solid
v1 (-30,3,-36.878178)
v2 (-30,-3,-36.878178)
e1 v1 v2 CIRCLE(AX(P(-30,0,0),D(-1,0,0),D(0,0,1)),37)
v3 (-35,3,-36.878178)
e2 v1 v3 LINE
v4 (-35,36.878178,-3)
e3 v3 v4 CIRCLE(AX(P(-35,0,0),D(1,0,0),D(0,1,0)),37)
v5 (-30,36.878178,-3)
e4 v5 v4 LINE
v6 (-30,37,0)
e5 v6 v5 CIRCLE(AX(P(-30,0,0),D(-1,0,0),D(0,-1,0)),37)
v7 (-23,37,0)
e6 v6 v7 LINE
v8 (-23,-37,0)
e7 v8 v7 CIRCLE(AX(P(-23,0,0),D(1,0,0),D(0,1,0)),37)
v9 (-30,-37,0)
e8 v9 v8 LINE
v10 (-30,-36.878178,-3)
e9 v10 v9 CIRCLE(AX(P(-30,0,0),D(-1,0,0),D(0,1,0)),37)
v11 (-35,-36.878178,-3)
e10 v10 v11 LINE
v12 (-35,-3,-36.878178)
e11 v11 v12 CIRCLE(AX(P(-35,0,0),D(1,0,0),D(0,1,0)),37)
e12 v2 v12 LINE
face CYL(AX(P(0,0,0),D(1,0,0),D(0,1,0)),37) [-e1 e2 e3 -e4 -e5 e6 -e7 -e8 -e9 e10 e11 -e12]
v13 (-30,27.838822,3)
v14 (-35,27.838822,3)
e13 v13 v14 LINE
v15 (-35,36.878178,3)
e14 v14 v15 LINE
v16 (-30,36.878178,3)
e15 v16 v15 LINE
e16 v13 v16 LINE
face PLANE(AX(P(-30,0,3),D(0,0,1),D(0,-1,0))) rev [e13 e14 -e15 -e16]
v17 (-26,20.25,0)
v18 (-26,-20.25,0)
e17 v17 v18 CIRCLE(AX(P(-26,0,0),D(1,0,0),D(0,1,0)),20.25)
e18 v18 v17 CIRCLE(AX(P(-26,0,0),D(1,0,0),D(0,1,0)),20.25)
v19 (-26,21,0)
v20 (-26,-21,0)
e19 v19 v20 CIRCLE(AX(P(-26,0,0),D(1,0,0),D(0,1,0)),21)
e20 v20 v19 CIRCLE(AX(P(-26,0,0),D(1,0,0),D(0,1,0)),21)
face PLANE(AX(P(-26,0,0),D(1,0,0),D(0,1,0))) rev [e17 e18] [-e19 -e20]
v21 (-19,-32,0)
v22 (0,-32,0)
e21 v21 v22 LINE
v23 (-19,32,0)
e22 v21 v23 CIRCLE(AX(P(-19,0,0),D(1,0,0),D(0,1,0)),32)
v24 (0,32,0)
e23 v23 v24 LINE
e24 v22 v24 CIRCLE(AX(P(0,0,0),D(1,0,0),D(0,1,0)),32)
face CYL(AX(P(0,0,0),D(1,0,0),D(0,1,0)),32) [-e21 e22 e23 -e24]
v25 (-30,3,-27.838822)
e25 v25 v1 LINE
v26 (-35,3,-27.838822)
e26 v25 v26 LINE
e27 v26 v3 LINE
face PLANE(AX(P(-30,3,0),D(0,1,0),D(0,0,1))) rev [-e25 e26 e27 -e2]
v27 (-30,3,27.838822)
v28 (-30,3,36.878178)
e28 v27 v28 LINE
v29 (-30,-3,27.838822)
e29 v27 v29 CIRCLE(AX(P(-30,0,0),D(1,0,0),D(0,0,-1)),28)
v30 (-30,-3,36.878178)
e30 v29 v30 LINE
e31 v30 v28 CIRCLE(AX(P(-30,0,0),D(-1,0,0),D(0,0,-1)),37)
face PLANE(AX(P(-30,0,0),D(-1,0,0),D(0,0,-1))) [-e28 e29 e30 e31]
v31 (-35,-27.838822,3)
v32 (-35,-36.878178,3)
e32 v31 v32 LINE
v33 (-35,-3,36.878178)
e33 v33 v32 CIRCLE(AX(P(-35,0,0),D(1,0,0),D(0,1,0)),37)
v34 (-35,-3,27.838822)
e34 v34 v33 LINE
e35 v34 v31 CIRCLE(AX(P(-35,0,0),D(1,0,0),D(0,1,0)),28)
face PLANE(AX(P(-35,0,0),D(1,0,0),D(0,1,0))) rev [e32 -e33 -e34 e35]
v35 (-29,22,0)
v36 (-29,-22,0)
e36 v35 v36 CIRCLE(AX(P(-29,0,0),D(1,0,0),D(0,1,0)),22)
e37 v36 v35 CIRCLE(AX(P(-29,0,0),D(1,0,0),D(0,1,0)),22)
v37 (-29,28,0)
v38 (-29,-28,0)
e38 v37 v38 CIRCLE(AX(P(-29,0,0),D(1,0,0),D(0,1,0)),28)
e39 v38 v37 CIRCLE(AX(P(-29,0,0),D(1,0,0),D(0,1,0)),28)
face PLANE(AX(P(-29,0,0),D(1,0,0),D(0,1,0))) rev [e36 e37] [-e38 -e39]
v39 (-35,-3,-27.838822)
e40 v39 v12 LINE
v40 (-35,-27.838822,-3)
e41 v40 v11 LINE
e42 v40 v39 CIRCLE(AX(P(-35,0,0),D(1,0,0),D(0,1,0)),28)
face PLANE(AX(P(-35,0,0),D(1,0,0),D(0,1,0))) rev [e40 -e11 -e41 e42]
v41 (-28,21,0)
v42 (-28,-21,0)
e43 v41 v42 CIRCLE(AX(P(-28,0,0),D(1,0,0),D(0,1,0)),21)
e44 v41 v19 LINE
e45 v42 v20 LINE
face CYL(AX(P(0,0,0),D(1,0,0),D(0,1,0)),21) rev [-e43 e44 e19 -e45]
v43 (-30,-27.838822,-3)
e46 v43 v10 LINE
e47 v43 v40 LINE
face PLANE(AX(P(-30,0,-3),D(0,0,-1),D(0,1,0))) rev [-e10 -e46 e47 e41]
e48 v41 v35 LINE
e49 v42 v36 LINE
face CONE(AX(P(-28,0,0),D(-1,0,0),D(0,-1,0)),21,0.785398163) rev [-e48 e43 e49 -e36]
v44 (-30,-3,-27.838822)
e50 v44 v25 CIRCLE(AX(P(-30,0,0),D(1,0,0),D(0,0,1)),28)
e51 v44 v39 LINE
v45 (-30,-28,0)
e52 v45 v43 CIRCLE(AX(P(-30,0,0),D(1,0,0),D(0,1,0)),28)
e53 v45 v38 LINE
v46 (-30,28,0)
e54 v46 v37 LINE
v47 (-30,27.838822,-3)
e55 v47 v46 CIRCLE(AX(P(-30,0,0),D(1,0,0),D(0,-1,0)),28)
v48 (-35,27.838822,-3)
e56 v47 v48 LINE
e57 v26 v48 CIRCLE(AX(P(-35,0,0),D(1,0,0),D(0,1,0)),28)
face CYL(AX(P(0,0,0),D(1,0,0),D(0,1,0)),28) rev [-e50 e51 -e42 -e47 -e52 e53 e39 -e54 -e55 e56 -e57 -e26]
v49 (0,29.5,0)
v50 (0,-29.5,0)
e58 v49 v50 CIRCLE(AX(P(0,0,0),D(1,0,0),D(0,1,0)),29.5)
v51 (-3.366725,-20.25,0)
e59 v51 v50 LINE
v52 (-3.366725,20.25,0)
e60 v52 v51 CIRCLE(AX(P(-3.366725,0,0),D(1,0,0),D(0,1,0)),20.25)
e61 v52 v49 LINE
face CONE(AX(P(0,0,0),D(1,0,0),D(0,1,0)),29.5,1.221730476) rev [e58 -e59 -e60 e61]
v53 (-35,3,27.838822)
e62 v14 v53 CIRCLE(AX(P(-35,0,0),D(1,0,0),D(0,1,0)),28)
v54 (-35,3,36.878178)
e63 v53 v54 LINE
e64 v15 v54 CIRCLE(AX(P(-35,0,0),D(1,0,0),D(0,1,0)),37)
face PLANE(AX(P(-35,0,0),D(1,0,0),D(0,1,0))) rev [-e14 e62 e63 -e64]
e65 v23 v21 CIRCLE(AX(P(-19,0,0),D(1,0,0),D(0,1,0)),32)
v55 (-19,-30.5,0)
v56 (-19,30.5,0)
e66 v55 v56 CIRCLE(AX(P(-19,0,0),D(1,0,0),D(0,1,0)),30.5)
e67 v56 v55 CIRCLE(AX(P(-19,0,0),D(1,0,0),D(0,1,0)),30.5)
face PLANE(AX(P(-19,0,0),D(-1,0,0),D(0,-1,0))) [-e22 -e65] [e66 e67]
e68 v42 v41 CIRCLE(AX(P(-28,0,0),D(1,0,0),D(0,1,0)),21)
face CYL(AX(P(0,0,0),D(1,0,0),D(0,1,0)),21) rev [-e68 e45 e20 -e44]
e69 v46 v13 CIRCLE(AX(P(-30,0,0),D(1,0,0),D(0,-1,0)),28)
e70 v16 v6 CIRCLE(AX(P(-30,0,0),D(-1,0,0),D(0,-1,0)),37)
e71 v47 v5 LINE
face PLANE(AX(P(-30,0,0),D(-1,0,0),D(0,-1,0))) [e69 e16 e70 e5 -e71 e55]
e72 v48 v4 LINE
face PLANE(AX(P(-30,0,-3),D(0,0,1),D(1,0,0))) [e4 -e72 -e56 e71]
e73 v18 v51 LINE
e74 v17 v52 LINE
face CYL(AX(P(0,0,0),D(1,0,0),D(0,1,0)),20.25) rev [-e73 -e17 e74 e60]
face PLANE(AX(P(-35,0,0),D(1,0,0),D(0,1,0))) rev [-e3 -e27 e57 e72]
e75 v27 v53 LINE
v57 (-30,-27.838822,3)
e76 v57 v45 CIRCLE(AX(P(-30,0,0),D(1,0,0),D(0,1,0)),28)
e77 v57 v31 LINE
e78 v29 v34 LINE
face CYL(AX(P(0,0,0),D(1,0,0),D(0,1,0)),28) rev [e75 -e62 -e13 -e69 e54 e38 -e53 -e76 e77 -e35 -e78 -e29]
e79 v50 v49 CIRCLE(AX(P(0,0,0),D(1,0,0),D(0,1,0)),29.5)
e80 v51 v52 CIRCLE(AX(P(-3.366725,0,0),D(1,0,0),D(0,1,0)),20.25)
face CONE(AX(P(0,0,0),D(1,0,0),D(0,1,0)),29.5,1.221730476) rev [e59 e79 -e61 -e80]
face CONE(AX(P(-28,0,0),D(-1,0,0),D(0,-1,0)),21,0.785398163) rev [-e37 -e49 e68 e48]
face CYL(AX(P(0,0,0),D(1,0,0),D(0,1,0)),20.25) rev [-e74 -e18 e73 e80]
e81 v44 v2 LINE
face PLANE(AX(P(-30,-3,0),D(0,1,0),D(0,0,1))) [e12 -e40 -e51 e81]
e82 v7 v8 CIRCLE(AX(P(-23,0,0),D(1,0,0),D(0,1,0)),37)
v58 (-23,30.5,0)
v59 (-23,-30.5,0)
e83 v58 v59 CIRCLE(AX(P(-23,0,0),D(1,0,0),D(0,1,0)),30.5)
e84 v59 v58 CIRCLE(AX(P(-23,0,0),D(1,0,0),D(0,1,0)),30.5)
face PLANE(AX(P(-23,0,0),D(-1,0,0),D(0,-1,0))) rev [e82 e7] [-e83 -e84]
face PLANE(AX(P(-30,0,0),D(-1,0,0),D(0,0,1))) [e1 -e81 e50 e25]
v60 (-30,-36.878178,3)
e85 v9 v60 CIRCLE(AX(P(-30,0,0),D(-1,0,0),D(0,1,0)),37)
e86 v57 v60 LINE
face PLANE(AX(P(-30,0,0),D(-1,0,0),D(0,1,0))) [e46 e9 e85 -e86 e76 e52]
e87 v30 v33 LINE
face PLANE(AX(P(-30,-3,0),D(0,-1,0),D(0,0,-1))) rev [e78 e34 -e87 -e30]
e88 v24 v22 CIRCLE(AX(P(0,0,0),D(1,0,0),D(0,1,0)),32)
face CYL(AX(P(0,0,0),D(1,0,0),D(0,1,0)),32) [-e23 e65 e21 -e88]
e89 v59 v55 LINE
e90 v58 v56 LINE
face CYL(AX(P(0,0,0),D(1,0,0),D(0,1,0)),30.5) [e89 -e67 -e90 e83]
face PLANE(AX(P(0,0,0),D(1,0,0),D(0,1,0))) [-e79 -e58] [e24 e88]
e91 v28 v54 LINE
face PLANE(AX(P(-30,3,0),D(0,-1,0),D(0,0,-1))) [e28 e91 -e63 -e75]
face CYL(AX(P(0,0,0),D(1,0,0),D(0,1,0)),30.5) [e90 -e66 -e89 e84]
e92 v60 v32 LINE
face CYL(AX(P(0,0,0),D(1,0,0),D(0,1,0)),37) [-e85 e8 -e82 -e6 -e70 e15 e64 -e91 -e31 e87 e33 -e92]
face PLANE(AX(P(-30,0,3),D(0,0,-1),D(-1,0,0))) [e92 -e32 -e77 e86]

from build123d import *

# Parameters (mm, degrees)
CUT_EXTRUDE1_DEPTH = 5
CIRPATTERN1_COUNT  = 4


with BuildPart() as part:
    # Sketch1 → Revolve1 (revolve)
    with BuildSketch(Plane.XY):
        Polygon((-3.366724667, 20.25), (0, 29.5), (0, 32), (-19, 32), (-19, 30.5), (-23, 30.5), (-23, 32), (-23, 37), (-35, 37), (-35, 28), (-29, 28), (-29, 22), (-28, 21), (-26, 21), (-26, 20.25), align=None)
    revolve(axis=Axis((0, 0, 0), (-1, 0, 0)))

    # Sketch2 → Cut-Extrude1 (cut)
    with BuildSketch(Plane.ZY.offset(35)):
        with BuildLine():
            ThreePointArc((3, 36.878177829), (0, 37), (-3, 36.878177829))
            Line((-3, 36.878177829), (-3, 27.838821814))
            ThreePointArc((-3, 27.838821814), (0, 28), (3, 27.838821814))
            Line((3, 27.838821814), (3, 36.878177829))
        make_face()
    cut_extrude1 = extrude(amount=-CUT_EXTRUDE1_DEPTH, mode=Mode.SUBTRACT)

    # CirPattern1: Cut-Extrude1 ×4 about axis
    cirpattern1_axis = Axis((0, 0, 0), (1, 0, 0))
    for i in range(1, CIRPATTERN1_COUNT):
        add(cut_extrude1.rotate(cirpattern1_axis, i * 360 / CIRPATTERN1_COUNT), mode=Mode.SUBTRACT)


solid = part.part
